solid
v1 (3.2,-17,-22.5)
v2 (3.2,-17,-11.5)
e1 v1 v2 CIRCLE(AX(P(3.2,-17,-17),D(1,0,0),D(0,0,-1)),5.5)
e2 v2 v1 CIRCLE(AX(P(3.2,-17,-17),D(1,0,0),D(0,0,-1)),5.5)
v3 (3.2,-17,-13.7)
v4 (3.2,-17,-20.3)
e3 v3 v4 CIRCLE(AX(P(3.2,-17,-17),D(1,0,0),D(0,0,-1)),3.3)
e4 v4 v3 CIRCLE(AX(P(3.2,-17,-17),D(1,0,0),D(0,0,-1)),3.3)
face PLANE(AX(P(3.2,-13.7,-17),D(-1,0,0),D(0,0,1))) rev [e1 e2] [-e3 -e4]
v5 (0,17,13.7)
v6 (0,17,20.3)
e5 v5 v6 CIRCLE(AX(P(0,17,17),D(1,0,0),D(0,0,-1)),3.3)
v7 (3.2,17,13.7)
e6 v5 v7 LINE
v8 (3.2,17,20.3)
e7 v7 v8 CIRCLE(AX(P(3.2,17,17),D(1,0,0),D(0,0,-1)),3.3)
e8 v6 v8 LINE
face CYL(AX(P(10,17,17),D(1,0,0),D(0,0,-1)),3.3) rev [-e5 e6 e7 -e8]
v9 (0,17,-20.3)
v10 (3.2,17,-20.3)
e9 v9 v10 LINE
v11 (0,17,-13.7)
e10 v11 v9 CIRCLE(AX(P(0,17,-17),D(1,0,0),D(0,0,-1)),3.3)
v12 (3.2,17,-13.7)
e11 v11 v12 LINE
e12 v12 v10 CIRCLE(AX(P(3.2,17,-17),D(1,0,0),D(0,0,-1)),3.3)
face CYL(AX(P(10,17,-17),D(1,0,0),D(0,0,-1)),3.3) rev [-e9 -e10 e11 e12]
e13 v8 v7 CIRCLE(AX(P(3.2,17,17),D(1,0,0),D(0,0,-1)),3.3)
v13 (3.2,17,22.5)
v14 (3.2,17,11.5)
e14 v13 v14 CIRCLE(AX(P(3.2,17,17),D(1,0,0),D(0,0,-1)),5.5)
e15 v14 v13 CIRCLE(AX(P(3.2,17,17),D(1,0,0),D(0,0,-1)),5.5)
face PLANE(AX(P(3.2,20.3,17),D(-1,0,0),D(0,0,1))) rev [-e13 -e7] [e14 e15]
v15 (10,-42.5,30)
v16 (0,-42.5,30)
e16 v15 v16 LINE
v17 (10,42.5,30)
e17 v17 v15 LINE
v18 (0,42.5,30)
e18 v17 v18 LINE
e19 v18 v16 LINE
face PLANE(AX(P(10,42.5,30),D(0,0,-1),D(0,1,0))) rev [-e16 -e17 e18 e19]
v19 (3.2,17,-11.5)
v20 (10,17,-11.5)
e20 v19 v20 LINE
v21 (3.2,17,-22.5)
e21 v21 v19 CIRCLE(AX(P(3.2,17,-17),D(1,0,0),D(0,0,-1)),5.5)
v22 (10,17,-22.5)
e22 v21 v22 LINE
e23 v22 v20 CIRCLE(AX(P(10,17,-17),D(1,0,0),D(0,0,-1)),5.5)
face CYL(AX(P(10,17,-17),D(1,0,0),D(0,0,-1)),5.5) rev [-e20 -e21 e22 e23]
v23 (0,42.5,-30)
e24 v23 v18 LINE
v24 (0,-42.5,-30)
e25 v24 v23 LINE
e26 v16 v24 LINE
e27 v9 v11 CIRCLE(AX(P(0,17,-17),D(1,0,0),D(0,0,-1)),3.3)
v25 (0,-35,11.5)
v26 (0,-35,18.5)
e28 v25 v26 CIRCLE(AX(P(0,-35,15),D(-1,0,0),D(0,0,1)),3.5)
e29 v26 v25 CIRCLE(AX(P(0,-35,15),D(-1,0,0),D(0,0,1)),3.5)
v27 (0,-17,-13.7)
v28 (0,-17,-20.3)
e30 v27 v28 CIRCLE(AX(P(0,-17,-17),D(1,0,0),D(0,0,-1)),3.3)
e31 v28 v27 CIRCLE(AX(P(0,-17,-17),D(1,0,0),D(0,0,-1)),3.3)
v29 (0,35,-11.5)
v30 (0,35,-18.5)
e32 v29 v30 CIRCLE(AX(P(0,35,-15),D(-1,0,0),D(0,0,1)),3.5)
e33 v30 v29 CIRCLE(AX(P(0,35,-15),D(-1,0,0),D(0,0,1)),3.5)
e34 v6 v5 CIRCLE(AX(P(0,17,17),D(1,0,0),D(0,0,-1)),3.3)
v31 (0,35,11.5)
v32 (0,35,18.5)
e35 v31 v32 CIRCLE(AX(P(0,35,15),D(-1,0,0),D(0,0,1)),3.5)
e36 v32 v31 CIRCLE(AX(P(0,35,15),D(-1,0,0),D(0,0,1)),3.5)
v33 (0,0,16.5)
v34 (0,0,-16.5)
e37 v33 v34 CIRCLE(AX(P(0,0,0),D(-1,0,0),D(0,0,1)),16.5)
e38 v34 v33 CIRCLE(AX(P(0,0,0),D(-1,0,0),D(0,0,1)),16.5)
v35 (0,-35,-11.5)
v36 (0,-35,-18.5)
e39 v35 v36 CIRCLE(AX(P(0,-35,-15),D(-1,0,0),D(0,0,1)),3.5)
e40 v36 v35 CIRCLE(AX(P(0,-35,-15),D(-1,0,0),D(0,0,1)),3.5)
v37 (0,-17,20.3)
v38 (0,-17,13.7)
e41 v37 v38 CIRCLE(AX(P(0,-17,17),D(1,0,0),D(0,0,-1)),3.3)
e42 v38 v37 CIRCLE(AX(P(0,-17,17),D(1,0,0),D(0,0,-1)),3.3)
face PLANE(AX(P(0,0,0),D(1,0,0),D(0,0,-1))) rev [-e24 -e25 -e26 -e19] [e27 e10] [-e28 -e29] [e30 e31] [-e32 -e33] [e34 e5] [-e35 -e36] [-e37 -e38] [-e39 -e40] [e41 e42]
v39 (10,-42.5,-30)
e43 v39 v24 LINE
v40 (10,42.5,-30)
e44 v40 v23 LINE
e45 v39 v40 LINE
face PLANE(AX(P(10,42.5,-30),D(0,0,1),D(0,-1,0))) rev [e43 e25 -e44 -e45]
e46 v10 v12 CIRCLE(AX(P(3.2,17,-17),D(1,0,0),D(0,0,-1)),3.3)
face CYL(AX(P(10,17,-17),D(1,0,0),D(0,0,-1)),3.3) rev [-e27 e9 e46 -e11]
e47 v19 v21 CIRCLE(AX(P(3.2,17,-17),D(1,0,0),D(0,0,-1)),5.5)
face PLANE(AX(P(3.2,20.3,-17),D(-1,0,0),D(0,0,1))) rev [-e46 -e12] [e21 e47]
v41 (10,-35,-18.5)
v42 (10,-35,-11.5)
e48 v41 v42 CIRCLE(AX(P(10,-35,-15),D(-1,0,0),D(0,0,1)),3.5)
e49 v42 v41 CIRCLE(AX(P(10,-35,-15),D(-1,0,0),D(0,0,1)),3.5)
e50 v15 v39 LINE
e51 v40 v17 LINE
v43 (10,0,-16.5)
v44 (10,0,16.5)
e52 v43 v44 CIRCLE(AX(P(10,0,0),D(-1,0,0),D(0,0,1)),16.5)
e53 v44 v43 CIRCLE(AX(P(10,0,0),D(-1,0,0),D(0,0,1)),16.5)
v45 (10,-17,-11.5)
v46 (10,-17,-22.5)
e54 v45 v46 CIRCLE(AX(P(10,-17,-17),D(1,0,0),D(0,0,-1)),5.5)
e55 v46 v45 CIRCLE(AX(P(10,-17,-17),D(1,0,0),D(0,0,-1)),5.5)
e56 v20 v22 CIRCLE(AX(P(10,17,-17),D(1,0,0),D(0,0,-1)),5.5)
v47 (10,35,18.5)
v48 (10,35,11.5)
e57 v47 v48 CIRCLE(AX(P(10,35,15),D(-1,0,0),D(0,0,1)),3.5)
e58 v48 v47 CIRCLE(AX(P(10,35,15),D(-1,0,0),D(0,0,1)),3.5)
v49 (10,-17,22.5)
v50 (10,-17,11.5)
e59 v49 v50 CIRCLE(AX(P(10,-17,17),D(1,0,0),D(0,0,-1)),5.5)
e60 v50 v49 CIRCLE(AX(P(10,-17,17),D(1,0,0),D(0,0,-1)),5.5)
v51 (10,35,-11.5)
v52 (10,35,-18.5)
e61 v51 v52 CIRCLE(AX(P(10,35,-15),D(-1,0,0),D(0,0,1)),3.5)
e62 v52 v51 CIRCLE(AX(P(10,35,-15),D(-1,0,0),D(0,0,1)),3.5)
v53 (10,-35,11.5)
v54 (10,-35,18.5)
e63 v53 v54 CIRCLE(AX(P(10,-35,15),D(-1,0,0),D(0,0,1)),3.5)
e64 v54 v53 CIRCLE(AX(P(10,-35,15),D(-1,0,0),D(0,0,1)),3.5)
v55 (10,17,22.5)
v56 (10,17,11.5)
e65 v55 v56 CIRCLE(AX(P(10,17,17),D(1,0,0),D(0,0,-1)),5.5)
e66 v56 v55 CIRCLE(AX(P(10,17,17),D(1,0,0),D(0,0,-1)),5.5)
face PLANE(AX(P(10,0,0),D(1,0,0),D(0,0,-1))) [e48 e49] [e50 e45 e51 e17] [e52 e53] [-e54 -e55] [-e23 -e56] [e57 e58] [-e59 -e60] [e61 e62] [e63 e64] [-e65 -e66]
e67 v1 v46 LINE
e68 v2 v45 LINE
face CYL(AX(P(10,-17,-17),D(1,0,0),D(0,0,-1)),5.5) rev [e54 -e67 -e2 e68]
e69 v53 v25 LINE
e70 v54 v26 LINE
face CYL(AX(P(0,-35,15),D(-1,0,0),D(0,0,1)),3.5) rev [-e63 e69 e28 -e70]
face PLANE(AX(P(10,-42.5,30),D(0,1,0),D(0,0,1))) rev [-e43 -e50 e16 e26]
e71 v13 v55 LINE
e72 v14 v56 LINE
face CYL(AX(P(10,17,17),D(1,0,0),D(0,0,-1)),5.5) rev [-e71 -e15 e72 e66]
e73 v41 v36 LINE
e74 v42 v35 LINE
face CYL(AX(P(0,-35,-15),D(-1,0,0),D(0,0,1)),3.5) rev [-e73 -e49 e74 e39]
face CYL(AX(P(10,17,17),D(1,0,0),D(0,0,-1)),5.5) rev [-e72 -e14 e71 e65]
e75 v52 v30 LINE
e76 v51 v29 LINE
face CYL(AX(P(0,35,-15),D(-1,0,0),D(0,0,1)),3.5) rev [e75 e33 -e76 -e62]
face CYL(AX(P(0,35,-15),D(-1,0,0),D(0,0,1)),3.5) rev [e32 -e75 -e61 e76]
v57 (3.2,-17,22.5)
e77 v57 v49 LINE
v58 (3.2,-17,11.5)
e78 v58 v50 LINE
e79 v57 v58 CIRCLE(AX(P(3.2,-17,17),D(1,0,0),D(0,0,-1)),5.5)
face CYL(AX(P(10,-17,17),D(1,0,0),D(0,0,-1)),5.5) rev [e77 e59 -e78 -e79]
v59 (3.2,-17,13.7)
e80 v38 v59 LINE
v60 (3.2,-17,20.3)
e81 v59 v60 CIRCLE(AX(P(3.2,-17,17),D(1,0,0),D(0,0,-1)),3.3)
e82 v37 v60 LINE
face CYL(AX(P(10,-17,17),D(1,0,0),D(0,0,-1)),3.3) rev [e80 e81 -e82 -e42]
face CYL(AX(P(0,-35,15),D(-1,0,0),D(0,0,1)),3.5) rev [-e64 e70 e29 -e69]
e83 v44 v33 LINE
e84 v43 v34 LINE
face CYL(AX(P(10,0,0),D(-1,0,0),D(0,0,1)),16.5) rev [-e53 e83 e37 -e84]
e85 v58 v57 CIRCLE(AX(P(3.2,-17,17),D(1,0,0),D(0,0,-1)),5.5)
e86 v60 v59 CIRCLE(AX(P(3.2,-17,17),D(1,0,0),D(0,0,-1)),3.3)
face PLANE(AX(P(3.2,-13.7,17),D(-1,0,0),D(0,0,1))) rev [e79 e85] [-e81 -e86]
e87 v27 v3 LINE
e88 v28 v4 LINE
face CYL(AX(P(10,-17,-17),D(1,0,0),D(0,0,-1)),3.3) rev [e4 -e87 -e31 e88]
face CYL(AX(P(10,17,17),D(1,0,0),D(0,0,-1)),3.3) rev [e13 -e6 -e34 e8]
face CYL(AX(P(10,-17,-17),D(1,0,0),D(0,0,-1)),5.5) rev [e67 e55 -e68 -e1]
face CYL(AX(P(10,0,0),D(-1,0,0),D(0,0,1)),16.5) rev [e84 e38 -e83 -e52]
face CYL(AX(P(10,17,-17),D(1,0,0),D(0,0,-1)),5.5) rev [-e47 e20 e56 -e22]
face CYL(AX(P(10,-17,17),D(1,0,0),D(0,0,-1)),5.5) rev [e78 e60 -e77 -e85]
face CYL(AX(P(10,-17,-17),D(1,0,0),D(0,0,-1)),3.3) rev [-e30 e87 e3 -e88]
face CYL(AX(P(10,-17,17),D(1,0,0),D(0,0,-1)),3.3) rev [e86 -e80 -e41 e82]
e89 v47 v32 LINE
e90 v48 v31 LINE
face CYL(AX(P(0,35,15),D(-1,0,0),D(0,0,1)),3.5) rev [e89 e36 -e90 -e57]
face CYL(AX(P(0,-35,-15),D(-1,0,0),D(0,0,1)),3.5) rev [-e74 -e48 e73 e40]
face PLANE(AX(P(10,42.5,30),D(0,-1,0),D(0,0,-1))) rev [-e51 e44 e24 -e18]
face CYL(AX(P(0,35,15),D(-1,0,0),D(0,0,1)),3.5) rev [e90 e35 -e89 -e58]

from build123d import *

# Parameters (mm, degrees)
SKETCH_1_W                = 60
SKETCH_1_H                = 85
EXTRUDE_1_DEPTH           = 10
HOLE_WIZARD_1_D           = 6.6
HOLE_WIZARD_1_CBORE_D     = 11
HOLE_WIZARD_1_CBORE_DEPTH = 6.8
HOLE_WIZARD_7_0_7_1_D     = 7
SKETCH_6_R                = 16.5
CUT_EXTRUDE_1_DEPTH       = 53.974050251


with BuildPart() as part:
    # 草图1 → 凸台-拉伸1 (new body)
    with BuildSketch(Plane(origin=(0, 0, 0), x_dir=(0, 0, -1), z_dir=(1, 0, 0))):
        Rectangle(SKETCH_1_W, SKETCH_1_H)
    extrude(amount=EXTRUDE_1_DEPTH)

    # 打孔尺寸(%根据)内六角圆柱头螺钉的类型1 (through all)
    with Locations(Plane(origin=(10, 0, 0), x_dir=(0, 0, -1), z_dir=(1, 0, 0))):
        with Locations((-17, 17), (17, 17), (-17, -17), (17, -17)):
            CounterBoreHole(HOLE_WIZARD_1_D / 2, HOLE_WIZARD_1_CBORE_D / 2, HOLE_WIZARD_1_CBORE_DEPTH)

    # Ø7.0 (7) 直径孔1 (through all)
    with Locations(Plane.ZY):
        with Locations((-15, 35), (15, 35), (-15, -35), (15, -35)):
            Hole(HOLE_WIZARD_7_0_7_1_D / 2)

    # 草图6 → 切除-拉伸1 (cut, through all)
    with BuildSketch(Plane.ZY):
        Circle(SKETCH_6_R)
    extrude(amount=-CUT_EXTRUDE_1_DEPTH, mode=Mode.SUBTRACT)


solid = part.part
